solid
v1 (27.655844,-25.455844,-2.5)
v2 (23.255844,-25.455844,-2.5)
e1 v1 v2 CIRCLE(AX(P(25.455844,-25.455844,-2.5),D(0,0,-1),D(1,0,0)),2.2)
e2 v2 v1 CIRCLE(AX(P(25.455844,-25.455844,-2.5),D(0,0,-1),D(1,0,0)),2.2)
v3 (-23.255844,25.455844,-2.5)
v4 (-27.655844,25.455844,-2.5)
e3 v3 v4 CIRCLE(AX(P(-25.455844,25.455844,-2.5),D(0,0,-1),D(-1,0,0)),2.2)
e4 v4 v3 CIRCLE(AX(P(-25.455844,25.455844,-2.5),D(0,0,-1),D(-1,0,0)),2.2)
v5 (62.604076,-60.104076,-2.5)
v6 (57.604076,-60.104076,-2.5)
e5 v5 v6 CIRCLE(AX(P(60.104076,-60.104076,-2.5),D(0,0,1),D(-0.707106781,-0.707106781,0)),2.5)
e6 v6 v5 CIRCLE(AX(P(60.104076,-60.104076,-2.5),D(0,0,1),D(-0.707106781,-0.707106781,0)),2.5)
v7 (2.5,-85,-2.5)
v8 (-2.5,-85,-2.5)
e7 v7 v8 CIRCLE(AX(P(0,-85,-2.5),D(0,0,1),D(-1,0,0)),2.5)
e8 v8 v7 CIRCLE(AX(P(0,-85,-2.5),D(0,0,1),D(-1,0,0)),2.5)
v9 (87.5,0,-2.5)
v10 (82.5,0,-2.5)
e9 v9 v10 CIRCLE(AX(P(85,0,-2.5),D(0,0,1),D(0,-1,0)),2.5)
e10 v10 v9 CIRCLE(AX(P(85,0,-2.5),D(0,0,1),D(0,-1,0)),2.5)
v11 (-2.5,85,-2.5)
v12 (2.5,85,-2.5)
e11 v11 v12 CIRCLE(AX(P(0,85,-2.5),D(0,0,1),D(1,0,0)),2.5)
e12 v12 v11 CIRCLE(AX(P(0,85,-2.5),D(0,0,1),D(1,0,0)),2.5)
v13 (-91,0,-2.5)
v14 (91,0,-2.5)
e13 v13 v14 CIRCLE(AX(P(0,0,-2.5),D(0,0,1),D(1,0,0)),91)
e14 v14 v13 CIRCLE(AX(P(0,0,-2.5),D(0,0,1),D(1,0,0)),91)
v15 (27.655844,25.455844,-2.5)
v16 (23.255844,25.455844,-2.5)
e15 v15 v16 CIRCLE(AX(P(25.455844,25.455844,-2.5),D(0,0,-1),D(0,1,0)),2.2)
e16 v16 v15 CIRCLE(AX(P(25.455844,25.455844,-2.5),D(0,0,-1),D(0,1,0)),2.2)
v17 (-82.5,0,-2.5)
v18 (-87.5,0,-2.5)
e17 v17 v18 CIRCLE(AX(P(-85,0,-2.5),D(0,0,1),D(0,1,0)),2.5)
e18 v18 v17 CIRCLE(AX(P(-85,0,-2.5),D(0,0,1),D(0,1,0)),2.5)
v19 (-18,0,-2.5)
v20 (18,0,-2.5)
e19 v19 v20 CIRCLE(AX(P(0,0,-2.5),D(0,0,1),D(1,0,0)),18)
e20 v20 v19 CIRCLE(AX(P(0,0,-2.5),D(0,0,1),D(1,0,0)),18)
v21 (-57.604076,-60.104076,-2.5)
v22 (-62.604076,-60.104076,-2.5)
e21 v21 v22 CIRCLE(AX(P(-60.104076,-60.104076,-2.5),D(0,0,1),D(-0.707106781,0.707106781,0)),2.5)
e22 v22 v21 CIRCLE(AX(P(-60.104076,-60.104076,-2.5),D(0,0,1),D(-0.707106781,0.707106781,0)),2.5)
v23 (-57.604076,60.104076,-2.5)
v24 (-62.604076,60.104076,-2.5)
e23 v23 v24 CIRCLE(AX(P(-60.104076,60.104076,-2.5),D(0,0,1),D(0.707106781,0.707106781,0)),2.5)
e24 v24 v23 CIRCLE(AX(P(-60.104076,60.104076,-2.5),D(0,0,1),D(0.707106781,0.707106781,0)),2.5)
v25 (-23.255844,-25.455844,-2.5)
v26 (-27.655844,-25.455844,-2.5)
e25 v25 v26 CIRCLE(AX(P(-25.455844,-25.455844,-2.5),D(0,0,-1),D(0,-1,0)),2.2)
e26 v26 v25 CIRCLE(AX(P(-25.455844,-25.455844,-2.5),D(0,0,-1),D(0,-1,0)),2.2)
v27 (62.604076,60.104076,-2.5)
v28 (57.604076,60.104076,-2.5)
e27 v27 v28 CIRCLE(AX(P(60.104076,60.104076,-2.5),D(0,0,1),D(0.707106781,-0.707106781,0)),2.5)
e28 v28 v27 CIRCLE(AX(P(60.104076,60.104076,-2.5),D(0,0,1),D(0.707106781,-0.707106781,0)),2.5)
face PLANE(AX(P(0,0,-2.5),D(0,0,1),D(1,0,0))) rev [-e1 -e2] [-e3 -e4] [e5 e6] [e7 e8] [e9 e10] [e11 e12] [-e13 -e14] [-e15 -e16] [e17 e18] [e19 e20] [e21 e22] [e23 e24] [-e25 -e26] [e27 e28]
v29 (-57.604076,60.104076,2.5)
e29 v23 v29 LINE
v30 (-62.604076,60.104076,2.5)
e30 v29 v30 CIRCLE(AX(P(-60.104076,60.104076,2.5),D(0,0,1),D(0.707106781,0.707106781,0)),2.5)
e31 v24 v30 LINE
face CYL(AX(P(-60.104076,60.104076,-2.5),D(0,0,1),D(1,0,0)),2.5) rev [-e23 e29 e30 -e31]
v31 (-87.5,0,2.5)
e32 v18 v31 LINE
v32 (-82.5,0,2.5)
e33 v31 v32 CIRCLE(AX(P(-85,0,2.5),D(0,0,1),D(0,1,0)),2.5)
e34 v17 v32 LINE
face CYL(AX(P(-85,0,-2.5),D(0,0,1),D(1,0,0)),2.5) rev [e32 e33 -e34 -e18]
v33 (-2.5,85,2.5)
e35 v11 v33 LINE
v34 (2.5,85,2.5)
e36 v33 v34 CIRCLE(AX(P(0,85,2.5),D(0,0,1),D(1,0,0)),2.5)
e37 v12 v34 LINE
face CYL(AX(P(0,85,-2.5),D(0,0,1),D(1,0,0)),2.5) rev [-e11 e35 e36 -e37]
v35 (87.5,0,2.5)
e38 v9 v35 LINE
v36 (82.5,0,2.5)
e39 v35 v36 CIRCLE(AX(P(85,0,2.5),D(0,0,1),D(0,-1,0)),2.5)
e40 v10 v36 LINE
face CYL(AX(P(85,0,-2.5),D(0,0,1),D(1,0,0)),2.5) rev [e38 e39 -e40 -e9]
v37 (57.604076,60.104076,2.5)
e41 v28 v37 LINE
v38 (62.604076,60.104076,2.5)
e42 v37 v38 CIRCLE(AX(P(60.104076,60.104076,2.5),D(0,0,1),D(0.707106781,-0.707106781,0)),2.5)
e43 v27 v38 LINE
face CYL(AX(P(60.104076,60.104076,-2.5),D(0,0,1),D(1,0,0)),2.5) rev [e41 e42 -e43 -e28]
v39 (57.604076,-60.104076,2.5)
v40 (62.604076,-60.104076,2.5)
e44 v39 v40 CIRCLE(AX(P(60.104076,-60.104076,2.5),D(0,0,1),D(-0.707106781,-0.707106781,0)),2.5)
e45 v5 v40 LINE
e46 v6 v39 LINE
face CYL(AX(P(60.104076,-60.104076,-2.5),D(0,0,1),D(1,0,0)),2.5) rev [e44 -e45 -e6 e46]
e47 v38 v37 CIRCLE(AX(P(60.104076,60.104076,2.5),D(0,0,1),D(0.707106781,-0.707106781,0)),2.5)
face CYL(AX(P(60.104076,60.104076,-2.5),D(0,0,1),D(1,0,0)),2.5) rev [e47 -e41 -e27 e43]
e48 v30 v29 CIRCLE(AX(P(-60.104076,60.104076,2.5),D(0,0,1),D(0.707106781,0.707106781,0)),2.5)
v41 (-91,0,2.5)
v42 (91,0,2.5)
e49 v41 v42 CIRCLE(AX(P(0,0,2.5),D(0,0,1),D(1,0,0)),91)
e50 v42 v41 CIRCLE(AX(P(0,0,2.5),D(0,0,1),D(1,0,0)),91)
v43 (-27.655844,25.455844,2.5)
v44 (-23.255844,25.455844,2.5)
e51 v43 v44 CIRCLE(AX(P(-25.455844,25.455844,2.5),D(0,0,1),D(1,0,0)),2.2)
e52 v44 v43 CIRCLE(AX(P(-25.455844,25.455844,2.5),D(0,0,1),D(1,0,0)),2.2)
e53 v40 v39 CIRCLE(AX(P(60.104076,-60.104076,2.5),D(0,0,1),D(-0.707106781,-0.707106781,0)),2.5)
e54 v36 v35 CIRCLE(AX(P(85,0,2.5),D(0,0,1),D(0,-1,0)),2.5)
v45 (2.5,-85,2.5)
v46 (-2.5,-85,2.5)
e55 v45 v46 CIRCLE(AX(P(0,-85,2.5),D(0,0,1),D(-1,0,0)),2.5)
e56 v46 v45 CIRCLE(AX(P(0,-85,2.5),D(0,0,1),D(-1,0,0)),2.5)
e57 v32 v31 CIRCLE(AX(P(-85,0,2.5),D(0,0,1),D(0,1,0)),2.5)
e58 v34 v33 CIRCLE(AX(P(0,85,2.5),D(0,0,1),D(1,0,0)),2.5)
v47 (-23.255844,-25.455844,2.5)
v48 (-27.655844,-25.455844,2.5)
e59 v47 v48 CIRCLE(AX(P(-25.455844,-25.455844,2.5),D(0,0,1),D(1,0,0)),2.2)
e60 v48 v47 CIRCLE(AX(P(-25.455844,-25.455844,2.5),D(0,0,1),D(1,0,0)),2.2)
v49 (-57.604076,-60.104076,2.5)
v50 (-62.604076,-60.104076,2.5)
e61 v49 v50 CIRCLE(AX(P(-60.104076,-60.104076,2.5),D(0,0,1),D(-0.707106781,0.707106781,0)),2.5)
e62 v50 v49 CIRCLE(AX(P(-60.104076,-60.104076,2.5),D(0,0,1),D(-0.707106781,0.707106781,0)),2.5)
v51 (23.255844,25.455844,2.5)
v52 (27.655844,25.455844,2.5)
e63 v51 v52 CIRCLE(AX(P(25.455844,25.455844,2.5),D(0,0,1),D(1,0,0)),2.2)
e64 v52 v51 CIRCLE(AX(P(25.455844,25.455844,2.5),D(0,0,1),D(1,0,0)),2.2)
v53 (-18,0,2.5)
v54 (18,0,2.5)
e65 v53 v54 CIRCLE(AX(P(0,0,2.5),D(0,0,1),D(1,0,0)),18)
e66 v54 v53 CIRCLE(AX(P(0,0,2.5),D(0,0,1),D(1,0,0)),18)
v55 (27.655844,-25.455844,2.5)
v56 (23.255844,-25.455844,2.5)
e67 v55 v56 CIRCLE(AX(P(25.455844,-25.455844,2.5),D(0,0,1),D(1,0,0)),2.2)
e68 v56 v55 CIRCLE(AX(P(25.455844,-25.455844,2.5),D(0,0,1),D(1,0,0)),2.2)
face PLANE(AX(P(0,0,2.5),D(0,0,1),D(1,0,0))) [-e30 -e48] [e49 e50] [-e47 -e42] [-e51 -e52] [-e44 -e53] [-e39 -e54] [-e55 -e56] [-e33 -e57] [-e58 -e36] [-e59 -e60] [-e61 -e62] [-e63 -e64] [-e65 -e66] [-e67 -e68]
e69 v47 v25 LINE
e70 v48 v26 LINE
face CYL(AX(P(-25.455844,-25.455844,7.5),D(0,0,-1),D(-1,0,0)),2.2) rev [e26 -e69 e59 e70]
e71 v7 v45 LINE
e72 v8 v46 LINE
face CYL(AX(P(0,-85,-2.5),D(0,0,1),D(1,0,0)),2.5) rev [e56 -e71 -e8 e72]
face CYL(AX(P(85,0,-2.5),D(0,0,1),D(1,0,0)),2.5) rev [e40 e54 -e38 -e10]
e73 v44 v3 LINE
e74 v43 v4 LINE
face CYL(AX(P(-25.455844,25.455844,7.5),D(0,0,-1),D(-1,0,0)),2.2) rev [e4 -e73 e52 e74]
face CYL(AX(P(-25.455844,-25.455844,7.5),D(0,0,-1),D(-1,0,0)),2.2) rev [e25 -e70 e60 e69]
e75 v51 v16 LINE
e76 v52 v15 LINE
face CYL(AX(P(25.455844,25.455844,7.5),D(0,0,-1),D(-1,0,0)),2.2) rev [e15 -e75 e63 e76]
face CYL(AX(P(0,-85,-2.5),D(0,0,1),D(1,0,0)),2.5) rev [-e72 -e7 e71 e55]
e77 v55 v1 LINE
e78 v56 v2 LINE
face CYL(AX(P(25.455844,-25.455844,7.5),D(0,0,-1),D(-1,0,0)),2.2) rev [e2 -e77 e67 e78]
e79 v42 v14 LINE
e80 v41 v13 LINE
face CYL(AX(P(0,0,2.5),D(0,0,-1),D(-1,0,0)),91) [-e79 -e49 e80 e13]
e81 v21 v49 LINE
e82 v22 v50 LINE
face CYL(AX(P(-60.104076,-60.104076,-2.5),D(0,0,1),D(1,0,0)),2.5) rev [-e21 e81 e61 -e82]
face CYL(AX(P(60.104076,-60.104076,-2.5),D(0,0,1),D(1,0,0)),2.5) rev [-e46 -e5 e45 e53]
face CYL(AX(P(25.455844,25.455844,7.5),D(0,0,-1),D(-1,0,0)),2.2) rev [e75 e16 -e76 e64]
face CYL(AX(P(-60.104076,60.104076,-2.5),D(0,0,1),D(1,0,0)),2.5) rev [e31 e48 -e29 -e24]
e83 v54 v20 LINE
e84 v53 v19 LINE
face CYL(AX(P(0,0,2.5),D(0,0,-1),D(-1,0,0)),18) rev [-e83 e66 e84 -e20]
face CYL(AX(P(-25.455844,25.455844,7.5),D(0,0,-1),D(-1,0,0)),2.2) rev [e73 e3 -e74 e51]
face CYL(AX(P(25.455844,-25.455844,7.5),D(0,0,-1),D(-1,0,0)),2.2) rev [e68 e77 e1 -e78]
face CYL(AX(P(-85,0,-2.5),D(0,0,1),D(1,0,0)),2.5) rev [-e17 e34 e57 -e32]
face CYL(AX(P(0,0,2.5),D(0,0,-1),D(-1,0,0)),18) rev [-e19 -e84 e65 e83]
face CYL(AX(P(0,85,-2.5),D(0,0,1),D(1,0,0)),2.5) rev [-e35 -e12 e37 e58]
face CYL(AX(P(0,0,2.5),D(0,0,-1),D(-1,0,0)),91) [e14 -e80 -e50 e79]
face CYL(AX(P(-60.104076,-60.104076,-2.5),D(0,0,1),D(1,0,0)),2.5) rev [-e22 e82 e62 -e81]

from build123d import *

# Parameters (mm, degrees)
SKETCH_1_R               = 91
SKETCH_1_R_2             = 18
EXTRUDE_1_DEPTH          = 2.5
SKETCH_2_R               = 2.5
CUT_EXTRUDE_1_DEPTH      = 5
PATTERN_CIRCULAR_1_COUNT = 8
SKETCH_3_R               = 2.2
CUT_EXTRUDE_2_DEPTH      = 10
PATTERN_CIRCULAR_2_COUNT = 4


with BuildPart() as part:
    # 草图1 → 凸台-拉伸1 (new, symmetric)
    with BuildSketch(Plane.XY):
        Circle(SKETCH_1_R)
        Circle(SKETCH_1_R_2, mode=Mode.SUBTRACT)
    extrude(amount=EXTRUDE_1_DEPTH, both=True)

    # 草图2 → 切除-拉伸1 (cut)
    with BuildSketch(Plane.XY.offset(2.5)):
        with Locations((0, 85)):
            Circle(SKETCH_2_R)
    cut_extrude_1 = extrude(amount=-CUT_EXTRUDE_1_DEPTH, mode=Mode.SUBTRACT)

    # 阵列(圆周)1: 切除-拉伸1 ×8 about axis
    pattern_circular_1_axis = Axis((0, 0, 0), (0, 0, 1))
    for i in range(1, PATTERN_CIRCULAR_1_COUNT):
        add(cut_extrude_1.rotate(pattern_circular_1_axis, i * 360 / PATTERN_CIRCULAR_1_COUNT), mode=Mode.SUBTRACT)

    # 草图3 → 切除-拉伸2 (cut)
    with BuildSketch(Plane(origin=(0, 0, -2.5), x_dir=(-1, 0, 0), z_dir=(0, 0, -1))):
        with Locations((25.455844123, 25.455844123)):
            Circle(SKETCH_3_R)
    cut_extrude_2 = extrude(amount=-CUT_EXTRUDE_2_DEPTH, mode=Mode.SUBTRACT)

    # 阵列(圆周)2: 切除-拉伸2 ×4 about axis
    pattern_circular_2_axis = Axis((0, 0, 0), (0, 0, 1))
    for i in range(1, PATTERN_CIRCULAR_2_COUNT):
        add(cut_extrude_2.rotate(pattern_circular_2_axis, i * 360 / PATTERN_CIRCULAR_2_COUNT), mode=Mode.SUBTRACT)


solid = part.part
